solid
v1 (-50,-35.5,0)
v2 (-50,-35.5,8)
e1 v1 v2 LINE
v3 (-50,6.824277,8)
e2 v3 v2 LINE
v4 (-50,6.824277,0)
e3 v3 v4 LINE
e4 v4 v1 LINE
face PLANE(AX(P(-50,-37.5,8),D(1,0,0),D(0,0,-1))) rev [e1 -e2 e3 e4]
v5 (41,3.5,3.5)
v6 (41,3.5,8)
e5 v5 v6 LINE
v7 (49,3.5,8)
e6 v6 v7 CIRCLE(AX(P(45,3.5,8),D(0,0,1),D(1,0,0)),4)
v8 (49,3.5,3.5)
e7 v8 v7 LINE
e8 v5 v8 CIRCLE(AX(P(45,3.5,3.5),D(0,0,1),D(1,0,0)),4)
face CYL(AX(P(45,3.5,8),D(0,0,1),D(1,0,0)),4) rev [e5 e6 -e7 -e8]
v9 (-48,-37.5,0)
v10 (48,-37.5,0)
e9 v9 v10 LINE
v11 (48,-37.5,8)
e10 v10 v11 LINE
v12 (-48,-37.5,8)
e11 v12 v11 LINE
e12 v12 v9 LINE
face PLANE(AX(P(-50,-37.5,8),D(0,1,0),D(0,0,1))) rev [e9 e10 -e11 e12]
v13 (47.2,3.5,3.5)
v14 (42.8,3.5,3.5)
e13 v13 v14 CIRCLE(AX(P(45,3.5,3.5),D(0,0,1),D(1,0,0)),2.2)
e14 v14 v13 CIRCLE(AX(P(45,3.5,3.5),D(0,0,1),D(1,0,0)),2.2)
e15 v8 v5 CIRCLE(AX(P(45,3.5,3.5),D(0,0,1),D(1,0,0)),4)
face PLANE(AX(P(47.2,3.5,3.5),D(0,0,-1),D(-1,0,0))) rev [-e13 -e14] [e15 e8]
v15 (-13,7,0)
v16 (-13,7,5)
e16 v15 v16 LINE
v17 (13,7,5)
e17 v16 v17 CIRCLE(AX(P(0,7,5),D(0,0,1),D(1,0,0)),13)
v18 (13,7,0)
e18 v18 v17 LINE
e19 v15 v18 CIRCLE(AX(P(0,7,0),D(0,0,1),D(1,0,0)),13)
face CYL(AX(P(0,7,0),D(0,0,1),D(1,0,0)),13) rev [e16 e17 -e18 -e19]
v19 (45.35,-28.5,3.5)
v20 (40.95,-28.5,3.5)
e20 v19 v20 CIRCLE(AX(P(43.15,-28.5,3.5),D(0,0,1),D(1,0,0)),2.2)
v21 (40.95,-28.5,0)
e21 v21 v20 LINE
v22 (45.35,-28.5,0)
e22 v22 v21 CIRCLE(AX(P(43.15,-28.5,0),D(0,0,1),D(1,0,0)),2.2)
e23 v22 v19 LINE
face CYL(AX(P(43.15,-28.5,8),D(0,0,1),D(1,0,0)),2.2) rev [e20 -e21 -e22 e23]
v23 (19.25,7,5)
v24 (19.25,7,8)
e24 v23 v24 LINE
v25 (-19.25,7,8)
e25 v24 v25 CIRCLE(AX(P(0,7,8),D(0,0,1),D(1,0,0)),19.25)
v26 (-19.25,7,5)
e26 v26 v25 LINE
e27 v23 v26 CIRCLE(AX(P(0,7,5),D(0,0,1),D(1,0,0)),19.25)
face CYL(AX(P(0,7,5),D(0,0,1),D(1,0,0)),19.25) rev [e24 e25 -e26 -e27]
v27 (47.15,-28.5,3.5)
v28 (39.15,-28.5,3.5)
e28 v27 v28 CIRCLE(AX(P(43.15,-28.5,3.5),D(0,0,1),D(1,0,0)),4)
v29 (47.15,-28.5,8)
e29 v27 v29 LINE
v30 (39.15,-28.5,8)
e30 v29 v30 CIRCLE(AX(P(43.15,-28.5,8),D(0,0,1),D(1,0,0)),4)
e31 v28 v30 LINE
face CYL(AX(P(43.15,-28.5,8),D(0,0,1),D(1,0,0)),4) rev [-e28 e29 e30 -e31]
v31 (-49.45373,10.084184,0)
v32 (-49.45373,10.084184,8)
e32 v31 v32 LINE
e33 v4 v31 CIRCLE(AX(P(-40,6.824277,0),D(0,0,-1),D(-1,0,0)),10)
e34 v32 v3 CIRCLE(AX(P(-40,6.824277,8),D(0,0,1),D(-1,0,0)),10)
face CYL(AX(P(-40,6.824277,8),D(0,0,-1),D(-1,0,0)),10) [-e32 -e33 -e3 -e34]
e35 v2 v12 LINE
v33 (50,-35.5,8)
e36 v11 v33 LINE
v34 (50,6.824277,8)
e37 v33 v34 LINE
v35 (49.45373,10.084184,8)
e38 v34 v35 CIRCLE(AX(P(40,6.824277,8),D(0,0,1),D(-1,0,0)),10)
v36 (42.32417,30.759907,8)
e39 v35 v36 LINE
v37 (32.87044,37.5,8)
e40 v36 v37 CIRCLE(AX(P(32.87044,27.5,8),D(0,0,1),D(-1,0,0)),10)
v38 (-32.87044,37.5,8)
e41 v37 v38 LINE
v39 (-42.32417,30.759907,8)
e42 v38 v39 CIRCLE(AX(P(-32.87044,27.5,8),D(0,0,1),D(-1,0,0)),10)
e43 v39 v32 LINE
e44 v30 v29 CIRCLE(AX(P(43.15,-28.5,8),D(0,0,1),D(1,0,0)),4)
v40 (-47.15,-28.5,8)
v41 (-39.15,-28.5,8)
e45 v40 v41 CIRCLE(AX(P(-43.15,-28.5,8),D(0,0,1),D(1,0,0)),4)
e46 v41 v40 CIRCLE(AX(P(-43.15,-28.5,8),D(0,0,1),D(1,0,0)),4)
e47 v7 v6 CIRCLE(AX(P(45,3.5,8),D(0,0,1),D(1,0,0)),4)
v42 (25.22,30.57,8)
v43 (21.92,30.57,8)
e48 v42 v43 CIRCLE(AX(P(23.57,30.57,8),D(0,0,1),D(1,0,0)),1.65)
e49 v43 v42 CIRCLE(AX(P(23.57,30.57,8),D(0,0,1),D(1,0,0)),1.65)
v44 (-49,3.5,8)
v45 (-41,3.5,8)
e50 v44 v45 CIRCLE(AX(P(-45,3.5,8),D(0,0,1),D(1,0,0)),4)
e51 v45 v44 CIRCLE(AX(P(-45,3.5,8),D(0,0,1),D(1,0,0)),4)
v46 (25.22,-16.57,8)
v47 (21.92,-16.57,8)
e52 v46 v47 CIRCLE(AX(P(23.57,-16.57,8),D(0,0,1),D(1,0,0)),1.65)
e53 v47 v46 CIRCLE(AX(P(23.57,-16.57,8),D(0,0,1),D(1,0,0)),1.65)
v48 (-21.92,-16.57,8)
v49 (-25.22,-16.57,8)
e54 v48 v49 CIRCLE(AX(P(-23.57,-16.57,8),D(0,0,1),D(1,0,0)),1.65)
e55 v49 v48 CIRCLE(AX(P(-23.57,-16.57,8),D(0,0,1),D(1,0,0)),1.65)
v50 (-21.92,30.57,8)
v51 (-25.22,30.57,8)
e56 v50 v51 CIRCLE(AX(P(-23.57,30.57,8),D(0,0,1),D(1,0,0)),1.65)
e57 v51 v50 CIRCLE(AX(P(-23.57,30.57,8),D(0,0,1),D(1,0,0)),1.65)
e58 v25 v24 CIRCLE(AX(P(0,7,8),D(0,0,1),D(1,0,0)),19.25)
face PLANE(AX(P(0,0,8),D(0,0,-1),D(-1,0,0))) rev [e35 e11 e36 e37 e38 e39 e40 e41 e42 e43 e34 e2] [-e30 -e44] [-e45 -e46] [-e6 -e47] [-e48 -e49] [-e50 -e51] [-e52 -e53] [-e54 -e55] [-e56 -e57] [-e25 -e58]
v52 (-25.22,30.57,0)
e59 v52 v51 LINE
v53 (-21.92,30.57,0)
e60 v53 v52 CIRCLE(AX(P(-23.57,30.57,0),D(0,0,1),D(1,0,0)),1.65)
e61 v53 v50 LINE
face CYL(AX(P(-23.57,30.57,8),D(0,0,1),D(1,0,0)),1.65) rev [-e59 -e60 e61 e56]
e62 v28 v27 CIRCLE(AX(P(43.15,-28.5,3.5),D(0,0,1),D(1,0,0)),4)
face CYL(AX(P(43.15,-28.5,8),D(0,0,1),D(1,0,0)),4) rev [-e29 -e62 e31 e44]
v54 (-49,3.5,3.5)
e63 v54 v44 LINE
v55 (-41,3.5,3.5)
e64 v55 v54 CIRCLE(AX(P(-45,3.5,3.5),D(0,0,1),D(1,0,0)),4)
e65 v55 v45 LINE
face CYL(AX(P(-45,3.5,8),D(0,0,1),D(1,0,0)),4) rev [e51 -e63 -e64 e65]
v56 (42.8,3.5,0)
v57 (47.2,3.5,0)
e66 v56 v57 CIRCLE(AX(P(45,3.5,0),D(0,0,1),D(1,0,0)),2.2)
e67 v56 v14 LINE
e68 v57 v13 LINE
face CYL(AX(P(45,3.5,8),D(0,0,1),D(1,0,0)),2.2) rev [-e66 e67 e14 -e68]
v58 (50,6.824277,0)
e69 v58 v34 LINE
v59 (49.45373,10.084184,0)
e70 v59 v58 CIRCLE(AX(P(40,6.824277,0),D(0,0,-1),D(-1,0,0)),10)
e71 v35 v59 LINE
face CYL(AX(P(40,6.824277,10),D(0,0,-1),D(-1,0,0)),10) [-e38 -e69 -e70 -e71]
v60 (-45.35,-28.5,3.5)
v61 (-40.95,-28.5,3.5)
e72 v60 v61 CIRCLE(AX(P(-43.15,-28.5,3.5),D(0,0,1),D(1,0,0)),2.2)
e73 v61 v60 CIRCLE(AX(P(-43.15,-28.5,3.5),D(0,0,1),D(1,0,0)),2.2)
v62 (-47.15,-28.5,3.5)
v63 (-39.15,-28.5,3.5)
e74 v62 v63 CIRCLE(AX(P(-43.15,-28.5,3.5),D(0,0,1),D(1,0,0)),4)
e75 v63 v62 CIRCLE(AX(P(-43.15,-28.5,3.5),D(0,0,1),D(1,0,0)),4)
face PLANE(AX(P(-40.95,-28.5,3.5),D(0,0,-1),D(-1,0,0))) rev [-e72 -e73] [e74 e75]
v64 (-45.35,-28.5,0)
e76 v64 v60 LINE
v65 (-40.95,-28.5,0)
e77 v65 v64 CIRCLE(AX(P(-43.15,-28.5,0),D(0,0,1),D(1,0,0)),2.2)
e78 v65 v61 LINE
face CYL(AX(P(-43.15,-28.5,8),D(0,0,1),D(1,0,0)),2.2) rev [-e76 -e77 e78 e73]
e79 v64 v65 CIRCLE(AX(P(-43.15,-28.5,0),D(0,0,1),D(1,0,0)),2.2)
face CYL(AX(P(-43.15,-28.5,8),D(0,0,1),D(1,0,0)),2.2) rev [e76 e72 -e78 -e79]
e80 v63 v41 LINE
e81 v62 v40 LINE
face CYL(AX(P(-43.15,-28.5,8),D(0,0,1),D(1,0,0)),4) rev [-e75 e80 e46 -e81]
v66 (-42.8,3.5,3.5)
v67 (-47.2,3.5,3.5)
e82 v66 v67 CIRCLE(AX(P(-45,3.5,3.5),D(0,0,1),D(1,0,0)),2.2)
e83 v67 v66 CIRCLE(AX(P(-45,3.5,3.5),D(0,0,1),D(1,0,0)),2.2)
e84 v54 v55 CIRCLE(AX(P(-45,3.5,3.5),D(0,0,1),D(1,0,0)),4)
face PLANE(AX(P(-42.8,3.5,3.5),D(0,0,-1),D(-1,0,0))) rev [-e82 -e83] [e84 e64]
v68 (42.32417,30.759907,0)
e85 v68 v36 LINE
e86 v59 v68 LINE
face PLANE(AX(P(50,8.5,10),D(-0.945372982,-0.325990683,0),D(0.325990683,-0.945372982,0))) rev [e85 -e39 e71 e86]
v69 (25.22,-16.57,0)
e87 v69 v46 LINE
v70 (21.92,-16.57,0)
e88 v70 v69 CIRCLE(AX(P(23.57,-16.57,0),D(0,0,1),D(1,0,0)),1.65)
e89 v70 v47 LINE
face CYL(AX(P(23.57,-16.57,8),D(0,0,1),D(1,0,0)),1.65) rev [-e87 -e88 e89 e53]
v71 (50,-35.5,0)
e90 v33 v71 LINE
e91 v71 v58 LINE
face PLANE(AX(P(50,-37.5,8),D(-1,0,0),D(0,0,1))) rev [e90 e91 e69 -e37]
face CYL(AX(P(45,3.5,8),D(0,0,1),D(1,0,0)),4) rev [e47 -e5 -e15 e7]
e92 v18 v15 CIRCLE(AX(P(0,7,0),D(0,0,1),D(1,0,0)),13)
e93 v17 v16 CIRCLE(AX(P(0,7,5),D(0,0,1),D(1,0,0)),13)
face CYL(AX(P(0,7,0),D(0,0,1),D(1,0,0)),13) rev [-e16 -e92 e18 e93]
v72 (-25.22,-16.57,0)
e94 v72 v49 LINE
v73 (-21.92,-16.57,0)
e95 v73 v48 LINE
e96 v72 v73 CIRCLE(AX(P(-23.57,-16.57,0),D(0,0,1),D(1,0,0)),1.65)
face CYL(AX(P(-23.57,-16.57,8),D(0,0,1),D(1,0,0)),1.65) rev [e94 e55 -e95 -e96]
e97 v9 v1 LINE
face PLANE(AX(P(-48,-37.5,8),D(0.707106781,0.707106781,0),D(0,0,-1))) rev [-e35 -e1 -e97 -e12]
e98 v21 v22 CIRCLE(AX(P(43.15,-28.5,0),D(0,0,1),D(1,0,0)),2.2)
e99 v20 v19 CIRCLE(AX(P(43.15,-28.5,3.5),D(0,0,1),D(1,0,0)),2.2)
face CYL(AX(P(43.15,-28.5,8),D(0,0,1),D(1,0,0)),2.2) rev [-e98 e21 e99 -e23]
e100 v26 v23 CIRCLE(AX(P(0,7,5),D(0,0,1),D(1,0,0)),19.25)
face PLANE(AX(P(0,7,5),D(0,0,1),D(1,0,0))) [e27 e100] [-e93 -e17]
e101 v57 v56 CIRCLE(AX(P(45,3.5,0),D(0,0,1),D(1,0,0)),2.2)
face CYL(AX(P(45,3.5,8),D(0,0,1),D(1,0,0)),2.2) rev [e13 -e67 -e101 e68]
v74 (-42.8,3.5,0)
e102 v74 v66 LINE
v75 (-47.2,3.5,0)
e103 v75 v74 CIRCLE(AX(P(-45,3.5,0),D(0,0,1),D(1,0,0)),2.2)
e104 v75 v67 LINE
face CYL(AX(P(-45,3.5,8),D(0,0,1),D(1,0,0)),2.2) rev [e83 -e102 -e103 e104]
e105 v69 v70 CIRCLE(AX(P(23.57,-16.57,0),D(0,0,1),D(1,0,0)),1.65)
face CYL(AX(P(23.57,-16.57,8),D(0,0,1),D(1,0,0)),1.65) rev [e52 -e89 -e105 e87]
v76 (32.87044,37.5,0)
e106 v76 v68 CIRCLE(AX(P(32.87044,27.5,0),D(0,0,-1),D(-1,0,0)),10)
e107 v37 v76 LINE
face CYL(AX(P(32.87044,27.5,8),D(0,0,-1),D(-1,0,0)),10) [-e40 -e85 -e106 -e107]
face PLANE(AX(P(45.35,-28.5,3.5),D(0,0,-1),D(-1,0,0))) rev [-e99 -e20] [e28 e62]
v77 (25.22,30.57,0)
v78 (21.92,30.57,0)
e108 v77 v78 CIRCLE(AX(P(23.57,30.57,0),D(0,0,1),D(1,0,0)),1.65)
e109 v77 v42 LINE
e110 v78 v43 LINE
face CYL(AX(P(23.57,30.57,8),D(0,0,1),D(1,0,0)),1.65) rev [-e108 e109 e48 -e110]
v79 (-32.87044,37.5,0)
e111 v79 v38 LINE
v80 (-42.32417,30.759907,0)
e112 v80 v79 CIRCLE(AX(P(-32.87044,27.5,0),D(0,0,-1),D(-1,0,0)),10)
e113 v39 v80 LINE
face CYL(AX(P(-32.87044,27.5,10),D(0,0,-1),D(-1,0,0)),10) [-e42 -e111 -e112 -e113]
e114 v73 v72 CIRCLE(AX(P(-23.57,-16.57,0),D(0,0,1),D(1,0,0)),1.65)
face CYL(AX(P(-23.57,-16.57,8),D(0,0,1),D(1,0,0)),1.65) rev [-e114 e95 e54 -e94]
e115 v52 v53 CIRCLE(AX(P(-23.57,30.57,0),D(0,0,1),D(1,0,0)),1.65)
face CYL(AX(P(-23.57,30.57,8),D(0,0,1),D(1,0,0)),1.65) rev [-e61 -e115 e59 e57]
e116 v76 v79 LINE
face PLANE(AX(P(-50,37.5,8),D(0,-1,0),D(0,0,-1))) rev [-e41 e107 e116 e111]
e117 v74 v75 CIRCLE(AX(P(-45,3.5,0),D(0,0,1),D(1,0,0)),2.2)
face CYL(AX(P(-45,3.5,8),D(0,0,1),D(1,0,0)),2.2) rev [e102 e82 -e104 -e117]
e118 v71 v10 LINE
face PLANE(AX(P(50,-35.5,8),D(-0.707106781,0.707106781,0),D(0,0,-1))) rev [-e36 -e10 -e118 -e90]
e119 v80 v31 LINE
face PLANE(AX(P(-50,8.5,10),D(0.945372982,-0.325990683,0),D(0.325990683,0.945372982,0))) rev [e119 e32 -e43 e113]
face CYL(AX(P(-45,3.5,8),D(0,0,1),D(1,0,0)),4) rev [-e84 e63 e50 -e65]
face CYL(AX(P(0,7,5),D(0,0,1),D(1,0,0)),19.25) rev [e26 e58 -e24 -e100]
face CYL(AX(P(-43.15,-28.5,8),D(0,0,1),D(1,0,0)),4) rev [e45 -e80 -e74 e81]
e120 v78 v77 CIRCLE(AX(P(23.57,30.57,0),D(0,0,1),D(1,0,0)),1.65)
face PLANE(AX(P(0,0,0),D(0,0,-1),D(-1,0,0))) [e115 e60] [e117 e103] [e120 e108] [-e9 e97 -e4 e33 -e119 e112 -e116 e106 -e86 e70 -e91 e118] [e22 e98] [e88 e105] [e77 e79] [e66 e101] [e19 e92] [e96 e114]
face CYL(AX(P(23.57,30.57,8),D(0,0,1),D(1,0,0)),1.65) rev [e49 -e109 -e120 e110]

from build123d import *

# Parameters (mm, degrees)
SKETCH_1_W                = 100
SKETCH_1_H                = 75
EXTRUDE_1_DEPTH           = 8
CUT_EXTRUDE_1_DEPTH       = 10
FILLET_1_R                = 10
CHAMFER_2_SIZE            = 2
SKETCH_6_R                = 19.25
CUT_EXTRUDE_2_DEPTH       = 3
SKETCH_7_R                = 13
CUT_EXTRUDE_3_DEPTH       = 63.69968102
HOLE_WIZARD_1_D           = 4.4
HOLE_WIZARD_1_CBORE_D     = 8
HOLE_WIZARD_1_CBORE_DEPTH = 4.5
HOLE_WIZARD_M4_1_D        = 3.3


with BuildPart() as part:
    # 草图1 → 凸台-拉伸1 (new body)
    with BuildSketch(Plane.XY):
        Rectangle(SKETCH_1_W, SKETCH_1_H)
    extrude(amount=EXTRUDE_1_DEPTH)

    # 草图3 → 切除-拉伸1 (cut)
    with BuildSketch(Plane(origin=(0, 0, 0), x_dir=(-1, 0, 0), z_dir=(0, 0, -1))):
        Polygon((-50, 8.5), (-40, 37.5), (-50, 37.5), align=None)
        Polygon((50, 37.5), (50, 8.5), (40, 37.5), align=None)
    extrude(amount=-CUT_EXTRUDE_1_DEPTH, mode=Mode.SUBTRACT)

    # 圆角1
    fillet_1_edges = [part.edges().sort_by_distance(p)[0] for p in [
        (50, 8.5, 4),
        (40, 37.5, 4),
        (-40, 37.5, 4),
        (-50, 8.5, 4),
    ]]
    fillet(fillet_1_edges, radius=FILLET_1_R)

    # 倒角2
    chamfer_2_edges = [part.edges().sort_by_distance(p)[0] for p in [
        (50, -37.5, 4),
        (-50, -37.5, 4),
    ]]
    chamfer(chamfer_2_edges, length=CHAMFER_2_SIZE)

    # 草图6 → 切除-拉伸2 (cut)
    with BuildSketch(Plane.XY.offset(8)):
        with Locations((0, 7)):
            Circle(SKETCH_6_R)
    extrude(amount=-CUT_EXTRUDE_2_DEPTH, mode=Mode.SUBTRACT)

    # 草图7 → 切除-拉伸3 (cut, through all)
    with BuildSketch(Plane.XY.offset(5)):
        with Locations((0, 7)):
            Circle(SKETCH_7_R)
    extrude(amount=-CUT_EXTRUDE_3_DEPTH, mode=Mode.SUBTRACT)

    # 打孔尺寸(%根据)内六角圆柱头螺钉的类型1 (through all)
    with Locations(Plane.XY.offset(8)):
        with Locations((-45, 3.5), (-43.15, -28.5), (43.15, -28.5), (45, 3.5)):
            CounterBoreHole(HOLE_WIZARD_1_D / 2, HOLE_WIZARD_1_CBORE_D / 2, HOLE_WIZARD_1_CBORE_DEPTH)

    # M4 螺纹孔1 (through all)
    with Locations(Plane.XY.offset(8)):
        with Locations((-23.57, -16.57), (23.57, -16.57), (23.57, 30.57), (-23.57, 30.57)):
            Hole(HOLE_WIZARD_M4_1_D / 2)


solid = part.part
